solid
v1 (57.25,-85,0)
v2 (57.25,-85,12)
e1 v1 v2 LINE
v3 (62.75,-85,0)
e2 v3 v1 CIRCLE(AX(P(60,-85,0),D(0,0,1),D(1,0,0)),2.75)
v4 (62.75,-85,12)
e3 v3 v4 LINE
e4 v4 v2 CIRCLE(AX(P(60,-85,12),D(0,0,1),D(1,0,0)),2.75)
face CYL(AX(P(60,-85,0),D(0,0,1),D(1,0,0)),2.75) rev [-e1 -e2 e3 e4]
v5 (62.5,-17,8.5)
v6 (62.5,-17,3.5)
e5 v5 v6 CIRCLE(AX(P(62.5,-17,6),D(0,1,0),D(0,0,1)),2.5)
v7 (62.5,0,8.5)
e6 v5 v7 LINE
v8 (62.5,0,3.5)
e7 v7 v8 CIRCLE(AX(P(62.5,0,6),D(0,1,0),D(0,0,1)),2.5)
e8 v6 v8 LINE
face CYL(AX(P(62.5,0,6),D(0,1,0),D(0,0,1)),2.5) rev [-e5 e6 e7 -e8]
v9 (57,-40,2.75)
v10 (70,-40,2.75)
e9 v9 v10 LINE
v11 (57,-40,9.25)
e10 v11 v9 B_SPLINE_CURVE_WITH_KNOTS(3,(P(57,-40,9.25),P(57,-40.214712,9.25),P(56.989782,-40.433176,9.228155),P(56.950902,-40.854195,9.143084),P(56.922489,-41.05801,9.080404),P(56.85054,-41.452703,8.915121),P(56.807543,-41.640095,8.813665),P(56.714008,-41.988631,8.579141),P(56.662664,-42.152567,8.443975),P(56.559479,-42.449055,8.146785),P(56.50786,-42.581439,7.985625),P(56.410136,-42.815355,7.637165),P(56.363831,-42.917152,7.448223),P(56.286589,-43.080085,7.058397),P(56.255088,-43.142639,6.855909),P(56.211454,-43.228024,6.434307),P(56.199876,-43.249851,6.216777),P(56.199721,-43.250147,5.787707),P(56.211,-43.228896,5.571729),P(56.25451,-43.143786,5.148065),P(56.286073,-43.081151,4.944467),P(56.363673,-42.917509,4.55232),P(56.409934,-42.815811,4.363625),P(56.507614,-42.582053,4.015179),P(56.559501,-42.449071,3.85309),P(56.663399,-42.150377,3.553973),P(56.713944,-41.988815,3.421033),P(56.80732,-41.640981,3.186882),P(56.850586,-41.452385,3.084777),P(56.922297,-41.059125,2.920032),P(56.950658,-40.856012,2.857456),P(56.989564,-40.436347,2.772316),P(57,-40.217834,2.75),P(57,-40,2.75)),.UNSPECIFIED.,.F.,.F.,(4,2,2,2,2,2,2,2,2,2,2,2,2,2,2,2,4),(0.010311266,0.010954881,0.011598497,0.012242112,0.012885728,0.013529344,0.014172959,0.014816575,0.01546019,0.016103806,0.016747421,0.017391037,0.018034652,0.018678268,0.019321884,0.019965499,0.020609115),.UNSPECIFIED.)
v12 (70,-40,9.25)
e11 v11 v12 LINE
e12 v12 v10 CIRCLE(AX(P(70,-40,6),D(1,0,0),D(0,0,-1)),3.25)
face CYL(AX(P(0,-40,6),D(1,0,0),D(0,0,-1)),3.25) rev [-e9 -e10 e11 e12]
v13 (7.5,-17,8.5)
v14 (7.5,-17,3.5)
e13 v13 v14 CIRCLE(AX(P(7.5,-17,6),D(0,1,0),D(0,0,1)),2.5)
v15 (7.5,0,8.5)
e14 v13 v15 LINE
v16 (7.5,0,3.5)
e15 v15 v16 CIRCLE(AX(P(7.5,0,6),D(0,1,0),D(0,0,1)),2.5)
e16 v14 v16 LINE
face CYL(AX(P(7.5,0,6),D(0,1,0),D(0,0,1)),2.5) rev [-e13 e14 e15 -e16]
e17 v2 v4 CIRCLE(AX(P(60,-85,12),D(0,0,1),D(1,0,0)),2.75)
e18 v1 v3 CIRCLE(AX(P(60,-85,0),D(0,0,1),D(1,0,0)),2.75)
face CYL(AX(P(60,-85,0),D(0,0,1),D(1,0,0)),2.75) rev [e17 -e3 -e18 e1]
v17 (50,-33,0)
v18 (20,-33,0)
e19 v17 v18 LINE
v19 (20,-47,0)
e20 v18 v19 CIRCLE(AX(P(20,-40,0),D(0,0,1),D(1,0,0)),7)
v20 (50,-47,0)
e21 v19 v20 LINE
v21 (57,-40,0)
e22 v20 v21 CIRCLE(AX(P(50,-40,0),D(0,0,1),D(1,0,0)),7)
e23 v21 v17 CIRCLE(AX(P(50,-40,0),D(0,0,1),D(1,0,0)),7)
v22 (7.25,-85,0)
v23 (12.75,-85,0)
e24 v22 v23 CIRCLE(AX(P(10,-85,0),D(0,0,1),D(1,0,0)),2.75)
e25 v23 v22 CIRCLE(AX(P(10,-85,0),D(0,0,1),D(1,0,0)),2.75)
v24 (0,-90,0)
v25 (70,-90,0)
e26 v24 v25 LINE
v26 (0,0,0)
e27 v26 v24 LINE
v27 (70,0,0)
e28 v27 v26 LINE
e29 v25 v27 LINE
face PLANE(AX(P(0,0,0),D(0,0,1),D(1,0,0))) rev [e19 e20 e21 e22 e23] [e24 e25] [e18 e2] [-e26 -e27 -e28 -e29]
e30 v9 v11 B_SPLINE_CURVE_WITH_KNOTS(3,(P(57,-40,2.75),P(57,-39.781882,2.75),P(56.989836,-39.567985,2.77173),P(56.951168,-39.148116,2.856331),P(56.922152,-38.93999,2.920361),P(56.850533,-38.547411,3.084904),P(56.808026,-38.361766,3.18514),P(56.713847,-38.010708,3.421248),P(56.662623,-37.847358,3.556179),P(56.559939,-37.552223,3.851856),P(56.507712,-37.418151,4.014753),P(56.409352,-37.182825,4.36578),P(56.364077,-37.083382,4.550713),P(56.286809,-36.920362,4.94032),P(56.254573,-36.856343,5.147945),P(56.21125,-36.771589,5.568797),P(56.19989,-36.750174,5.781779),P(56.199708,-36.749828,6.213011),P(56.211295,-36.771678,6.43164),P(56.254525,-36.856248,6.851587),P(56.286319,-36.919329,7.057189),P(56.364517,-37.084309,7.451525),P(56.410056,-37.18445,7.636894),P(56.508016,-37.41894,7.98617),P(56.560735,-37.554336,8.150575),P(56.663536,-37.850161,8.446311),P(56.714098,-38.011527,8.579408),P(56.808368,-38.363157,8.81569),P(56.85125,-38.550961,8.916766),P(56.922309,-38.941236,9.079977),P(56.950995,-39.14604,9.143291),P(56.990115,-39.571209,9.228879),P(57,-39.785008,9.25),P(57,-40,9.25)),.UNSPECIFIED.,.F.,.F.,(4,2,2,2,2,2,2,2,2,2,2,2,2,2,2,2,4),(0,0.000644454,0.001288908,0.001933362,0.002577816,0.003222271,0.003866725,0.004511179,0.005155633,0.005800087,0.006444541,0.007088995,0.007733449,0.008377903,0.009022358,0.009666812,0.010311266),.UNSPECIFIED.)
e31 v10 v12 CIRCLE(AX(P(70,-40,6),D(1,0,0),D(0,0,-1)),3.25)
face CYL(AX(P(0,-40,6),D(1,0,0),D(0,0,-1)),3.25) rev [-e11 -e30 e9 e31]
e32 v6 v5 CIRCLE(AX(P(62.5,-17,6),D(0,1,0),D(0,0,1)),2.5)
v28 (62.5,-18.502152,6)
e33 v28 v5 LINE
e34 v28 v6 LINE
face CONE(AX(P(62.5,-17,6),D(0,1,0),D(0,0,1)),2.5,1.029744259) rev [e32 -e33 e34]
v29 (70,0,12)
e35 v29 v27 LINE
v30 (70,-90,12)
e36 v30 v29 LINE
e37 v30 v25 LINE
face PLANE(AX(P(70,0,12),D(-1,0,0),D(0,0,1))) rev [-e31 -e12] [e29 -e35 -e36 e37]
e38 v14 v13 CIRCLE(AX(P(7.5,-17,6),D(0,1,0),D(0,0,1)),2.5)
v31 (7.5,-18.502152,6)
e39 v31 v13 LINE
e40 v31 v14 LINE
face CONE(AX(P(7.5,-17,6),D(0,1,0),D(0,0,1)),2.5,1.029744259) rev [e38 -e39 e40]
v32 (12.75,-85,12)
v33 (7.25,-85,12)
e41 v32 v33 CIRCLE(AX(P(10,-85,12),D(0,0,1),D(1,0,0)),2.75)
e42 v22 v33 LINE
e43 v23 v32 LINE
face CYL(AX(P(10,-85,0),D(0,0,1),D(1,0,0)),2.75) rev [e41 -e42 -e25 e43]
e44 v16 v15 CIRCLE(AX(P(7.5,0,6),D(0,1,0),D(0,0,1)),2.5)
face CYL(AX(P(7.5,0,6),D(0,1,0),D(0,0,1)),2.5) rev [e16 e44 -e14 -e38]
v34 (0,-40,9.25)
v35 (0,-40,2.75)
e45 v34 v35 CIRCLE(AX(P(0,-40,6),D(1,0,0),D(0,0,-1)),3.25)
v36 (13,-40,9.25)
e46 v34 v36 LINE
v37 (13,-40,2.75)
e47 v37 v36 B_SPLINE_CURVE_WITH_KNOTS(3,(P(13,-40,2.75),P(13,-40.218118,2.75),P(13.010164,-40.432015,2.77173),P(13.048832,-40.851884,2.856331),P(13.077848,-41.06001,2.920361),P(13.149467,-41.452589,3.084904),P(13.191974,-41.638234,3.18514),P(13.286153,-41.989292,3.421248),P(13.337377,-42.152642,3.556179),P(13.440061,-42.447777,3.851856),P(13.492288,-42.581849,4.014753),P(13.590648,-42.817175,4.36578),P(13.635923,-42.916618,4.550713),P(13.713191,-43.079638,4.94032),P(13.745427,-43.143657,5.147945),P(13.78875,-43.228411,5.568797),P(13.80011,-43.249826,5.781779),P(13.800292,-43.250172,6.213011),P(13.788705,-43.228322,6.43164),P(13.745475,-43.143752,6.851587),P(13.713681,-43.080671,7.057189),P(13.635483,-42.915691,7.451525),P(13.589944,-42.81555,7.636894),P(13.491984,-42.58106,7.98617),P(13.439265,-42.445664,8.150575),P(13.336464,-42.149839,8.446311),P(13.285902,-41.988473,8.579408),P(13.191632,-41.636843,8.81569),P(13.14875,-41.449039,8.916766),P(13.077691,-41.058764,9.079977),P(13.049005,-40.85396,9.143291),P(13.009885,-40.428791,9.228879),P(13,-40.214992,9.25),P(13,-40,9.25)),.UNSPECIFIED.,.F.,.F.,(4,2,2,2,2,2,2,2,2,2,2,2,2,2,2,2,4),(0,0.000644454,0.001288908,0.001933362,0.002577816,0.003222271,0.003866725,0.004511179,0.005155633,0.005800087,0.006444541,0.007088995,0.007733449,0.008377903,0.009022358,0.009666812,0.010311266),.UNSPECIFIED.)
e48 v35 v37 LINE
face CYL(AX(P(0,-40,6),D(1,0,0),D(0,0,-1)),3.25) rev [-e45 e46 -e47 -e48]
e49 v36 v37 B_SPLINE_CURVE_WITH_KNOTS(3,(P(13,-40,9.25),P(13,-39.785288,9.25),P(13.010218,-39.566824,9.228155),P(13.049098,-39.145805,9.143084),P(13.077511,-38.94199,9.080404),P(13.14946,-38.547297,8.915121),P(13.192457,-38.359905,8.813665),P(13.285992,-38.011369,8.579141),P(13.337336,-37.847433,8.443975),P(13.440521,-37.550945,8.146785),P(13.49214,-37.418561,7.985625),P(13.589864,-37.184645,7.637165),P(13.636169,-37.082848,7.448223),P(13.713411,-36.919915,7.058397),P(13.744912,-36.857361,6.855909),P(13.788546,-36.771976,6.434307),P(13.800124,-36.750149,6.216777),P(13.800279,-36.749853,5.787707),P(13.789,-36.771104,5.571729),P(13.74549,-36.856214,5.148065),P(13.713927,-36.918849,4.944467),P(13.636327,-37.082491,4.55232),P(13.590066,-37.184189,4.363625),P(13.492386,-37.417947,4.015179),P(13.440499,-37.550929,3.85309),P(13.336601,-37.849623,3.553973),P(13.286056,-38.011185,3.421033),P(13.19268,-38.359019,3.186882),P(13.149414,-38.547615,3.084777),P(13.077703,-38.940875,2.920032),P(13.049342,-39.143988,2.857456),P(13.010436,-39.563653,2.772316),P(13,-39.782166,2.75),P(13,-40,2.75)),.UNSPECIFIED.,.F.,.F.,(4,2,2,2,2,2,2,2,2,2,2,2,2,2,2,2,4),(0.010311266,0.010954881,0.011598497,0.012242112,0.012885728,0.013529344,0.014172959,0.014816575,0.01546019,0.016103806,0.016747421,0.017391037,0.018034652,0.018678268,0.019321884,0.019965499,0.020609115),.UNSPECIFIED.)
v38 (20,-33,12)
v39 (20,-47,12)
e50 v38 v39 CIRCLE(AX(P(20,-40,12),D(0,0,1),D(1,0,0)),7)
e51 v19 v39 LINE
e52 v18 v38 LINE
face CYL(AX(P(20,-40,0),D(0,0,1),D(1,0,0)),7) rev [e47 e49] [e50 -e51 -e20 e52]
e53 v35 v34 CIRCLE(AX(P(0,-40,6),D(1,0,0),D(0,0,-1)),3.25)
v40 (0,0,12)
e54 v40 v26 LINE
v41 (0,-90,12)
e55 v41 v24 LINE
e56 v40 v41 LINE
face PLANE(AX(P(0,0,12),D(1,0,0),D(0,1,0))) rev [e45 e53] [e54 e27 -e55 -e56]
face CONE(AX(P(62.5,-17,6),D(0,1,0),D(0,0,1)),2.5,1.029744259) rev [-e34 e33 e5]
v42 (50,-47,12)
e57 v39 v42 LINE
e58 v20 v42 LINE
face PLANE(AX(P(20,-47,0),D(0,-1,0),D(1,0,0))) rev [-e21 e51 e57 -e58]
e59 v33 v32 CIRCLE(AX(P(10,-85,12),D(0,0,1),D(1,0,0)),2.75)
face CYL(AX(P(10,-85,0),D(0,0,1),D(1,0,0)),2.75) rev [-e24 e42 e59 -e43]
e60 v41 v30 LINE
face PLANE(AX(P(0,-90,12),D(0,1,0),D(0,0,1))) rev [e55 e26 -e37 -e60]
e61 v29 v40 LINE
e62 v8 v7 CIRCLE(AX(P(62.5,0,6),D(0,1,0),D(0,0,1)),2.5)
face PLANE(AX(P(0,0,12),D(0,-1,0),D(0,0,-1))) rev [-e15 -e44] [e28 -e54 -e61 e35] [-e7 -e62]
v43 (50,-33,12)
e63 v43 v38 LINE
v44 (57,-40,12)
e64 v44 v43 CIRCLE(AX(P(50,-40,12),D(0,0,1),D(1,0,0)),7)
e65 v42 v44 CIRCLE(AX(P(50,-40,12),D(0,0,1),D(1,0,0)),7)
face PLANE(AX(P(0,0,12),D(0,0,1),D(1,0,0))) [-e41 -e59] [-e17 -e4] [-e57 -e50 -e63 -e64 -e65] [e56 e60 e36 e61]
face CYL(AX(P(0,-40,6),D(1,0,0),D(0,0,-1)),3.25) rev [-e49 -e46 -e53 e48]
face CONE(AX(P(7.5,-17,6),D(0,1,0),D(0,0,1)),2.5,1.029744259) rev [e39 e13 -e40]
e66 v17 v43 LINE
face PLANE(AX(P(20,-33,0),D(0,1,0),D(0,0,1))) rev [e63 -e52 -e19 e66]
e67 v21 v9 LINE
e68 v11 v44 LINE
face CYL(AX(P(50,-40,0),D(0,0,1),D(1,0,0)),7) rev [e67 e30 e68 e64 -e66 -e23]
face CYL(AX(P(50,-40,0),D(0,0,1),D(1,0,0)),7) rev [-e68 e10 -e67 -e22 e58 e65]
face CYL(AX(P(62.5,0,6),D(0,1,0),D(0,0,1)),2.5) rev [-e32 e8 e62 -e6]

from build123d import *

# Parameters (mm, degrees)
SKETCH_1_W             = 70
SKETCH_1_H             = 90
EXTRUDE_1_DEPTH        = 12
CUT_EXTRUDE_1_DEPTH    = 115.647285184
SKETCH_4_R             = 3.25
CUT_EXTRUDE_2_DEPTH    = 115.647285184
HOLE_WIZARD_M6_1_D     = 5
HOLE_WIZARD_M6_1_DEPTH = 17
HOLE_WIZARD_M6_1_TIP   = 1.502151548
SKETCH_11_R            = 2.75
CUT_EXTRUDE_3_DEPTH    = 115.647285255


with BuildPart() as part:
    # 草图1 → 凸台-拉伸1 (new body)
    with BuildSketch(Plane.XY):
        with Locations((35, -45)):
            Rectangle(SKETCH_1_W, SKETCH_1_H)
    extrude(amount=EXTRUDE_1_DEPTH)

    # 草图2 → 切除-拉伸1 (cut, through all)
    with BuildSketch(Plane.XY.offset(12)):
        with BuildLine():
            Line((20, -33), (50, -33))
            ThreePointArc((50, -33), (57, -40), (50, -47))
            Line((50, -47), (20, -47))
            ThreePointArc((20, -47), (13, -40), (20, -33))
        make_face()
    extrude(amount=-CUT_EXTRUDE_1_DEPTH, mode=Mode.SUBTRACT)

    # 草图4 → 切除-拉伸2 (cut, through all)
    with BuildSketch(Plane(origin=(70, 0, 0), x_dir=(0, 0, -1), z_dir=(1, 0, 0))):
        with Locations((-6, -40)):
            Circle(SKETCH_4_R)
    extrude(amount=-CUT_EXTRUDE_2_DEPTH, mode=Mode.SUBTRACT)

    # M6 螺纹孔1
    with Locations(Plane(origin=(0, 0, 0), x_dir=(1, 0, 0), z_dir=(0, 1, 0))):
        with Locations((62.5, -6), (7.5, -6)):
            Hole(HOLE_WIZARD_M6_1_D / 2, depth=HOLE_WIZARD_M6_1_DEPTH)
            with Locations((0, 0, -(HOLE_WIZARD_M6_1_DEPTH + HOLE_WIZARD_M6_1_TIP / 2))):  # 118° drill point
                Cone(0, HOLE_WIZARD_M6_1_D / 2, HOLE_WIZARD_M6_1_TIP, mode=Mode.SUBTRACT)

    # 草图11 → 切除-拉伸3 (cut, through all)
    with BuildSketch(Plane.XY.offset(12)):
        with Locations((10, -85)):
            Circle(SKETCH_11_R)
        with Locations((60, -85)):
            Circle(SKETCH_11_R)
    extrude(amount=-CUT_EXTRUDE_3_DEPTH, mode=Mode.SUBTRACT)


solid = part.part
